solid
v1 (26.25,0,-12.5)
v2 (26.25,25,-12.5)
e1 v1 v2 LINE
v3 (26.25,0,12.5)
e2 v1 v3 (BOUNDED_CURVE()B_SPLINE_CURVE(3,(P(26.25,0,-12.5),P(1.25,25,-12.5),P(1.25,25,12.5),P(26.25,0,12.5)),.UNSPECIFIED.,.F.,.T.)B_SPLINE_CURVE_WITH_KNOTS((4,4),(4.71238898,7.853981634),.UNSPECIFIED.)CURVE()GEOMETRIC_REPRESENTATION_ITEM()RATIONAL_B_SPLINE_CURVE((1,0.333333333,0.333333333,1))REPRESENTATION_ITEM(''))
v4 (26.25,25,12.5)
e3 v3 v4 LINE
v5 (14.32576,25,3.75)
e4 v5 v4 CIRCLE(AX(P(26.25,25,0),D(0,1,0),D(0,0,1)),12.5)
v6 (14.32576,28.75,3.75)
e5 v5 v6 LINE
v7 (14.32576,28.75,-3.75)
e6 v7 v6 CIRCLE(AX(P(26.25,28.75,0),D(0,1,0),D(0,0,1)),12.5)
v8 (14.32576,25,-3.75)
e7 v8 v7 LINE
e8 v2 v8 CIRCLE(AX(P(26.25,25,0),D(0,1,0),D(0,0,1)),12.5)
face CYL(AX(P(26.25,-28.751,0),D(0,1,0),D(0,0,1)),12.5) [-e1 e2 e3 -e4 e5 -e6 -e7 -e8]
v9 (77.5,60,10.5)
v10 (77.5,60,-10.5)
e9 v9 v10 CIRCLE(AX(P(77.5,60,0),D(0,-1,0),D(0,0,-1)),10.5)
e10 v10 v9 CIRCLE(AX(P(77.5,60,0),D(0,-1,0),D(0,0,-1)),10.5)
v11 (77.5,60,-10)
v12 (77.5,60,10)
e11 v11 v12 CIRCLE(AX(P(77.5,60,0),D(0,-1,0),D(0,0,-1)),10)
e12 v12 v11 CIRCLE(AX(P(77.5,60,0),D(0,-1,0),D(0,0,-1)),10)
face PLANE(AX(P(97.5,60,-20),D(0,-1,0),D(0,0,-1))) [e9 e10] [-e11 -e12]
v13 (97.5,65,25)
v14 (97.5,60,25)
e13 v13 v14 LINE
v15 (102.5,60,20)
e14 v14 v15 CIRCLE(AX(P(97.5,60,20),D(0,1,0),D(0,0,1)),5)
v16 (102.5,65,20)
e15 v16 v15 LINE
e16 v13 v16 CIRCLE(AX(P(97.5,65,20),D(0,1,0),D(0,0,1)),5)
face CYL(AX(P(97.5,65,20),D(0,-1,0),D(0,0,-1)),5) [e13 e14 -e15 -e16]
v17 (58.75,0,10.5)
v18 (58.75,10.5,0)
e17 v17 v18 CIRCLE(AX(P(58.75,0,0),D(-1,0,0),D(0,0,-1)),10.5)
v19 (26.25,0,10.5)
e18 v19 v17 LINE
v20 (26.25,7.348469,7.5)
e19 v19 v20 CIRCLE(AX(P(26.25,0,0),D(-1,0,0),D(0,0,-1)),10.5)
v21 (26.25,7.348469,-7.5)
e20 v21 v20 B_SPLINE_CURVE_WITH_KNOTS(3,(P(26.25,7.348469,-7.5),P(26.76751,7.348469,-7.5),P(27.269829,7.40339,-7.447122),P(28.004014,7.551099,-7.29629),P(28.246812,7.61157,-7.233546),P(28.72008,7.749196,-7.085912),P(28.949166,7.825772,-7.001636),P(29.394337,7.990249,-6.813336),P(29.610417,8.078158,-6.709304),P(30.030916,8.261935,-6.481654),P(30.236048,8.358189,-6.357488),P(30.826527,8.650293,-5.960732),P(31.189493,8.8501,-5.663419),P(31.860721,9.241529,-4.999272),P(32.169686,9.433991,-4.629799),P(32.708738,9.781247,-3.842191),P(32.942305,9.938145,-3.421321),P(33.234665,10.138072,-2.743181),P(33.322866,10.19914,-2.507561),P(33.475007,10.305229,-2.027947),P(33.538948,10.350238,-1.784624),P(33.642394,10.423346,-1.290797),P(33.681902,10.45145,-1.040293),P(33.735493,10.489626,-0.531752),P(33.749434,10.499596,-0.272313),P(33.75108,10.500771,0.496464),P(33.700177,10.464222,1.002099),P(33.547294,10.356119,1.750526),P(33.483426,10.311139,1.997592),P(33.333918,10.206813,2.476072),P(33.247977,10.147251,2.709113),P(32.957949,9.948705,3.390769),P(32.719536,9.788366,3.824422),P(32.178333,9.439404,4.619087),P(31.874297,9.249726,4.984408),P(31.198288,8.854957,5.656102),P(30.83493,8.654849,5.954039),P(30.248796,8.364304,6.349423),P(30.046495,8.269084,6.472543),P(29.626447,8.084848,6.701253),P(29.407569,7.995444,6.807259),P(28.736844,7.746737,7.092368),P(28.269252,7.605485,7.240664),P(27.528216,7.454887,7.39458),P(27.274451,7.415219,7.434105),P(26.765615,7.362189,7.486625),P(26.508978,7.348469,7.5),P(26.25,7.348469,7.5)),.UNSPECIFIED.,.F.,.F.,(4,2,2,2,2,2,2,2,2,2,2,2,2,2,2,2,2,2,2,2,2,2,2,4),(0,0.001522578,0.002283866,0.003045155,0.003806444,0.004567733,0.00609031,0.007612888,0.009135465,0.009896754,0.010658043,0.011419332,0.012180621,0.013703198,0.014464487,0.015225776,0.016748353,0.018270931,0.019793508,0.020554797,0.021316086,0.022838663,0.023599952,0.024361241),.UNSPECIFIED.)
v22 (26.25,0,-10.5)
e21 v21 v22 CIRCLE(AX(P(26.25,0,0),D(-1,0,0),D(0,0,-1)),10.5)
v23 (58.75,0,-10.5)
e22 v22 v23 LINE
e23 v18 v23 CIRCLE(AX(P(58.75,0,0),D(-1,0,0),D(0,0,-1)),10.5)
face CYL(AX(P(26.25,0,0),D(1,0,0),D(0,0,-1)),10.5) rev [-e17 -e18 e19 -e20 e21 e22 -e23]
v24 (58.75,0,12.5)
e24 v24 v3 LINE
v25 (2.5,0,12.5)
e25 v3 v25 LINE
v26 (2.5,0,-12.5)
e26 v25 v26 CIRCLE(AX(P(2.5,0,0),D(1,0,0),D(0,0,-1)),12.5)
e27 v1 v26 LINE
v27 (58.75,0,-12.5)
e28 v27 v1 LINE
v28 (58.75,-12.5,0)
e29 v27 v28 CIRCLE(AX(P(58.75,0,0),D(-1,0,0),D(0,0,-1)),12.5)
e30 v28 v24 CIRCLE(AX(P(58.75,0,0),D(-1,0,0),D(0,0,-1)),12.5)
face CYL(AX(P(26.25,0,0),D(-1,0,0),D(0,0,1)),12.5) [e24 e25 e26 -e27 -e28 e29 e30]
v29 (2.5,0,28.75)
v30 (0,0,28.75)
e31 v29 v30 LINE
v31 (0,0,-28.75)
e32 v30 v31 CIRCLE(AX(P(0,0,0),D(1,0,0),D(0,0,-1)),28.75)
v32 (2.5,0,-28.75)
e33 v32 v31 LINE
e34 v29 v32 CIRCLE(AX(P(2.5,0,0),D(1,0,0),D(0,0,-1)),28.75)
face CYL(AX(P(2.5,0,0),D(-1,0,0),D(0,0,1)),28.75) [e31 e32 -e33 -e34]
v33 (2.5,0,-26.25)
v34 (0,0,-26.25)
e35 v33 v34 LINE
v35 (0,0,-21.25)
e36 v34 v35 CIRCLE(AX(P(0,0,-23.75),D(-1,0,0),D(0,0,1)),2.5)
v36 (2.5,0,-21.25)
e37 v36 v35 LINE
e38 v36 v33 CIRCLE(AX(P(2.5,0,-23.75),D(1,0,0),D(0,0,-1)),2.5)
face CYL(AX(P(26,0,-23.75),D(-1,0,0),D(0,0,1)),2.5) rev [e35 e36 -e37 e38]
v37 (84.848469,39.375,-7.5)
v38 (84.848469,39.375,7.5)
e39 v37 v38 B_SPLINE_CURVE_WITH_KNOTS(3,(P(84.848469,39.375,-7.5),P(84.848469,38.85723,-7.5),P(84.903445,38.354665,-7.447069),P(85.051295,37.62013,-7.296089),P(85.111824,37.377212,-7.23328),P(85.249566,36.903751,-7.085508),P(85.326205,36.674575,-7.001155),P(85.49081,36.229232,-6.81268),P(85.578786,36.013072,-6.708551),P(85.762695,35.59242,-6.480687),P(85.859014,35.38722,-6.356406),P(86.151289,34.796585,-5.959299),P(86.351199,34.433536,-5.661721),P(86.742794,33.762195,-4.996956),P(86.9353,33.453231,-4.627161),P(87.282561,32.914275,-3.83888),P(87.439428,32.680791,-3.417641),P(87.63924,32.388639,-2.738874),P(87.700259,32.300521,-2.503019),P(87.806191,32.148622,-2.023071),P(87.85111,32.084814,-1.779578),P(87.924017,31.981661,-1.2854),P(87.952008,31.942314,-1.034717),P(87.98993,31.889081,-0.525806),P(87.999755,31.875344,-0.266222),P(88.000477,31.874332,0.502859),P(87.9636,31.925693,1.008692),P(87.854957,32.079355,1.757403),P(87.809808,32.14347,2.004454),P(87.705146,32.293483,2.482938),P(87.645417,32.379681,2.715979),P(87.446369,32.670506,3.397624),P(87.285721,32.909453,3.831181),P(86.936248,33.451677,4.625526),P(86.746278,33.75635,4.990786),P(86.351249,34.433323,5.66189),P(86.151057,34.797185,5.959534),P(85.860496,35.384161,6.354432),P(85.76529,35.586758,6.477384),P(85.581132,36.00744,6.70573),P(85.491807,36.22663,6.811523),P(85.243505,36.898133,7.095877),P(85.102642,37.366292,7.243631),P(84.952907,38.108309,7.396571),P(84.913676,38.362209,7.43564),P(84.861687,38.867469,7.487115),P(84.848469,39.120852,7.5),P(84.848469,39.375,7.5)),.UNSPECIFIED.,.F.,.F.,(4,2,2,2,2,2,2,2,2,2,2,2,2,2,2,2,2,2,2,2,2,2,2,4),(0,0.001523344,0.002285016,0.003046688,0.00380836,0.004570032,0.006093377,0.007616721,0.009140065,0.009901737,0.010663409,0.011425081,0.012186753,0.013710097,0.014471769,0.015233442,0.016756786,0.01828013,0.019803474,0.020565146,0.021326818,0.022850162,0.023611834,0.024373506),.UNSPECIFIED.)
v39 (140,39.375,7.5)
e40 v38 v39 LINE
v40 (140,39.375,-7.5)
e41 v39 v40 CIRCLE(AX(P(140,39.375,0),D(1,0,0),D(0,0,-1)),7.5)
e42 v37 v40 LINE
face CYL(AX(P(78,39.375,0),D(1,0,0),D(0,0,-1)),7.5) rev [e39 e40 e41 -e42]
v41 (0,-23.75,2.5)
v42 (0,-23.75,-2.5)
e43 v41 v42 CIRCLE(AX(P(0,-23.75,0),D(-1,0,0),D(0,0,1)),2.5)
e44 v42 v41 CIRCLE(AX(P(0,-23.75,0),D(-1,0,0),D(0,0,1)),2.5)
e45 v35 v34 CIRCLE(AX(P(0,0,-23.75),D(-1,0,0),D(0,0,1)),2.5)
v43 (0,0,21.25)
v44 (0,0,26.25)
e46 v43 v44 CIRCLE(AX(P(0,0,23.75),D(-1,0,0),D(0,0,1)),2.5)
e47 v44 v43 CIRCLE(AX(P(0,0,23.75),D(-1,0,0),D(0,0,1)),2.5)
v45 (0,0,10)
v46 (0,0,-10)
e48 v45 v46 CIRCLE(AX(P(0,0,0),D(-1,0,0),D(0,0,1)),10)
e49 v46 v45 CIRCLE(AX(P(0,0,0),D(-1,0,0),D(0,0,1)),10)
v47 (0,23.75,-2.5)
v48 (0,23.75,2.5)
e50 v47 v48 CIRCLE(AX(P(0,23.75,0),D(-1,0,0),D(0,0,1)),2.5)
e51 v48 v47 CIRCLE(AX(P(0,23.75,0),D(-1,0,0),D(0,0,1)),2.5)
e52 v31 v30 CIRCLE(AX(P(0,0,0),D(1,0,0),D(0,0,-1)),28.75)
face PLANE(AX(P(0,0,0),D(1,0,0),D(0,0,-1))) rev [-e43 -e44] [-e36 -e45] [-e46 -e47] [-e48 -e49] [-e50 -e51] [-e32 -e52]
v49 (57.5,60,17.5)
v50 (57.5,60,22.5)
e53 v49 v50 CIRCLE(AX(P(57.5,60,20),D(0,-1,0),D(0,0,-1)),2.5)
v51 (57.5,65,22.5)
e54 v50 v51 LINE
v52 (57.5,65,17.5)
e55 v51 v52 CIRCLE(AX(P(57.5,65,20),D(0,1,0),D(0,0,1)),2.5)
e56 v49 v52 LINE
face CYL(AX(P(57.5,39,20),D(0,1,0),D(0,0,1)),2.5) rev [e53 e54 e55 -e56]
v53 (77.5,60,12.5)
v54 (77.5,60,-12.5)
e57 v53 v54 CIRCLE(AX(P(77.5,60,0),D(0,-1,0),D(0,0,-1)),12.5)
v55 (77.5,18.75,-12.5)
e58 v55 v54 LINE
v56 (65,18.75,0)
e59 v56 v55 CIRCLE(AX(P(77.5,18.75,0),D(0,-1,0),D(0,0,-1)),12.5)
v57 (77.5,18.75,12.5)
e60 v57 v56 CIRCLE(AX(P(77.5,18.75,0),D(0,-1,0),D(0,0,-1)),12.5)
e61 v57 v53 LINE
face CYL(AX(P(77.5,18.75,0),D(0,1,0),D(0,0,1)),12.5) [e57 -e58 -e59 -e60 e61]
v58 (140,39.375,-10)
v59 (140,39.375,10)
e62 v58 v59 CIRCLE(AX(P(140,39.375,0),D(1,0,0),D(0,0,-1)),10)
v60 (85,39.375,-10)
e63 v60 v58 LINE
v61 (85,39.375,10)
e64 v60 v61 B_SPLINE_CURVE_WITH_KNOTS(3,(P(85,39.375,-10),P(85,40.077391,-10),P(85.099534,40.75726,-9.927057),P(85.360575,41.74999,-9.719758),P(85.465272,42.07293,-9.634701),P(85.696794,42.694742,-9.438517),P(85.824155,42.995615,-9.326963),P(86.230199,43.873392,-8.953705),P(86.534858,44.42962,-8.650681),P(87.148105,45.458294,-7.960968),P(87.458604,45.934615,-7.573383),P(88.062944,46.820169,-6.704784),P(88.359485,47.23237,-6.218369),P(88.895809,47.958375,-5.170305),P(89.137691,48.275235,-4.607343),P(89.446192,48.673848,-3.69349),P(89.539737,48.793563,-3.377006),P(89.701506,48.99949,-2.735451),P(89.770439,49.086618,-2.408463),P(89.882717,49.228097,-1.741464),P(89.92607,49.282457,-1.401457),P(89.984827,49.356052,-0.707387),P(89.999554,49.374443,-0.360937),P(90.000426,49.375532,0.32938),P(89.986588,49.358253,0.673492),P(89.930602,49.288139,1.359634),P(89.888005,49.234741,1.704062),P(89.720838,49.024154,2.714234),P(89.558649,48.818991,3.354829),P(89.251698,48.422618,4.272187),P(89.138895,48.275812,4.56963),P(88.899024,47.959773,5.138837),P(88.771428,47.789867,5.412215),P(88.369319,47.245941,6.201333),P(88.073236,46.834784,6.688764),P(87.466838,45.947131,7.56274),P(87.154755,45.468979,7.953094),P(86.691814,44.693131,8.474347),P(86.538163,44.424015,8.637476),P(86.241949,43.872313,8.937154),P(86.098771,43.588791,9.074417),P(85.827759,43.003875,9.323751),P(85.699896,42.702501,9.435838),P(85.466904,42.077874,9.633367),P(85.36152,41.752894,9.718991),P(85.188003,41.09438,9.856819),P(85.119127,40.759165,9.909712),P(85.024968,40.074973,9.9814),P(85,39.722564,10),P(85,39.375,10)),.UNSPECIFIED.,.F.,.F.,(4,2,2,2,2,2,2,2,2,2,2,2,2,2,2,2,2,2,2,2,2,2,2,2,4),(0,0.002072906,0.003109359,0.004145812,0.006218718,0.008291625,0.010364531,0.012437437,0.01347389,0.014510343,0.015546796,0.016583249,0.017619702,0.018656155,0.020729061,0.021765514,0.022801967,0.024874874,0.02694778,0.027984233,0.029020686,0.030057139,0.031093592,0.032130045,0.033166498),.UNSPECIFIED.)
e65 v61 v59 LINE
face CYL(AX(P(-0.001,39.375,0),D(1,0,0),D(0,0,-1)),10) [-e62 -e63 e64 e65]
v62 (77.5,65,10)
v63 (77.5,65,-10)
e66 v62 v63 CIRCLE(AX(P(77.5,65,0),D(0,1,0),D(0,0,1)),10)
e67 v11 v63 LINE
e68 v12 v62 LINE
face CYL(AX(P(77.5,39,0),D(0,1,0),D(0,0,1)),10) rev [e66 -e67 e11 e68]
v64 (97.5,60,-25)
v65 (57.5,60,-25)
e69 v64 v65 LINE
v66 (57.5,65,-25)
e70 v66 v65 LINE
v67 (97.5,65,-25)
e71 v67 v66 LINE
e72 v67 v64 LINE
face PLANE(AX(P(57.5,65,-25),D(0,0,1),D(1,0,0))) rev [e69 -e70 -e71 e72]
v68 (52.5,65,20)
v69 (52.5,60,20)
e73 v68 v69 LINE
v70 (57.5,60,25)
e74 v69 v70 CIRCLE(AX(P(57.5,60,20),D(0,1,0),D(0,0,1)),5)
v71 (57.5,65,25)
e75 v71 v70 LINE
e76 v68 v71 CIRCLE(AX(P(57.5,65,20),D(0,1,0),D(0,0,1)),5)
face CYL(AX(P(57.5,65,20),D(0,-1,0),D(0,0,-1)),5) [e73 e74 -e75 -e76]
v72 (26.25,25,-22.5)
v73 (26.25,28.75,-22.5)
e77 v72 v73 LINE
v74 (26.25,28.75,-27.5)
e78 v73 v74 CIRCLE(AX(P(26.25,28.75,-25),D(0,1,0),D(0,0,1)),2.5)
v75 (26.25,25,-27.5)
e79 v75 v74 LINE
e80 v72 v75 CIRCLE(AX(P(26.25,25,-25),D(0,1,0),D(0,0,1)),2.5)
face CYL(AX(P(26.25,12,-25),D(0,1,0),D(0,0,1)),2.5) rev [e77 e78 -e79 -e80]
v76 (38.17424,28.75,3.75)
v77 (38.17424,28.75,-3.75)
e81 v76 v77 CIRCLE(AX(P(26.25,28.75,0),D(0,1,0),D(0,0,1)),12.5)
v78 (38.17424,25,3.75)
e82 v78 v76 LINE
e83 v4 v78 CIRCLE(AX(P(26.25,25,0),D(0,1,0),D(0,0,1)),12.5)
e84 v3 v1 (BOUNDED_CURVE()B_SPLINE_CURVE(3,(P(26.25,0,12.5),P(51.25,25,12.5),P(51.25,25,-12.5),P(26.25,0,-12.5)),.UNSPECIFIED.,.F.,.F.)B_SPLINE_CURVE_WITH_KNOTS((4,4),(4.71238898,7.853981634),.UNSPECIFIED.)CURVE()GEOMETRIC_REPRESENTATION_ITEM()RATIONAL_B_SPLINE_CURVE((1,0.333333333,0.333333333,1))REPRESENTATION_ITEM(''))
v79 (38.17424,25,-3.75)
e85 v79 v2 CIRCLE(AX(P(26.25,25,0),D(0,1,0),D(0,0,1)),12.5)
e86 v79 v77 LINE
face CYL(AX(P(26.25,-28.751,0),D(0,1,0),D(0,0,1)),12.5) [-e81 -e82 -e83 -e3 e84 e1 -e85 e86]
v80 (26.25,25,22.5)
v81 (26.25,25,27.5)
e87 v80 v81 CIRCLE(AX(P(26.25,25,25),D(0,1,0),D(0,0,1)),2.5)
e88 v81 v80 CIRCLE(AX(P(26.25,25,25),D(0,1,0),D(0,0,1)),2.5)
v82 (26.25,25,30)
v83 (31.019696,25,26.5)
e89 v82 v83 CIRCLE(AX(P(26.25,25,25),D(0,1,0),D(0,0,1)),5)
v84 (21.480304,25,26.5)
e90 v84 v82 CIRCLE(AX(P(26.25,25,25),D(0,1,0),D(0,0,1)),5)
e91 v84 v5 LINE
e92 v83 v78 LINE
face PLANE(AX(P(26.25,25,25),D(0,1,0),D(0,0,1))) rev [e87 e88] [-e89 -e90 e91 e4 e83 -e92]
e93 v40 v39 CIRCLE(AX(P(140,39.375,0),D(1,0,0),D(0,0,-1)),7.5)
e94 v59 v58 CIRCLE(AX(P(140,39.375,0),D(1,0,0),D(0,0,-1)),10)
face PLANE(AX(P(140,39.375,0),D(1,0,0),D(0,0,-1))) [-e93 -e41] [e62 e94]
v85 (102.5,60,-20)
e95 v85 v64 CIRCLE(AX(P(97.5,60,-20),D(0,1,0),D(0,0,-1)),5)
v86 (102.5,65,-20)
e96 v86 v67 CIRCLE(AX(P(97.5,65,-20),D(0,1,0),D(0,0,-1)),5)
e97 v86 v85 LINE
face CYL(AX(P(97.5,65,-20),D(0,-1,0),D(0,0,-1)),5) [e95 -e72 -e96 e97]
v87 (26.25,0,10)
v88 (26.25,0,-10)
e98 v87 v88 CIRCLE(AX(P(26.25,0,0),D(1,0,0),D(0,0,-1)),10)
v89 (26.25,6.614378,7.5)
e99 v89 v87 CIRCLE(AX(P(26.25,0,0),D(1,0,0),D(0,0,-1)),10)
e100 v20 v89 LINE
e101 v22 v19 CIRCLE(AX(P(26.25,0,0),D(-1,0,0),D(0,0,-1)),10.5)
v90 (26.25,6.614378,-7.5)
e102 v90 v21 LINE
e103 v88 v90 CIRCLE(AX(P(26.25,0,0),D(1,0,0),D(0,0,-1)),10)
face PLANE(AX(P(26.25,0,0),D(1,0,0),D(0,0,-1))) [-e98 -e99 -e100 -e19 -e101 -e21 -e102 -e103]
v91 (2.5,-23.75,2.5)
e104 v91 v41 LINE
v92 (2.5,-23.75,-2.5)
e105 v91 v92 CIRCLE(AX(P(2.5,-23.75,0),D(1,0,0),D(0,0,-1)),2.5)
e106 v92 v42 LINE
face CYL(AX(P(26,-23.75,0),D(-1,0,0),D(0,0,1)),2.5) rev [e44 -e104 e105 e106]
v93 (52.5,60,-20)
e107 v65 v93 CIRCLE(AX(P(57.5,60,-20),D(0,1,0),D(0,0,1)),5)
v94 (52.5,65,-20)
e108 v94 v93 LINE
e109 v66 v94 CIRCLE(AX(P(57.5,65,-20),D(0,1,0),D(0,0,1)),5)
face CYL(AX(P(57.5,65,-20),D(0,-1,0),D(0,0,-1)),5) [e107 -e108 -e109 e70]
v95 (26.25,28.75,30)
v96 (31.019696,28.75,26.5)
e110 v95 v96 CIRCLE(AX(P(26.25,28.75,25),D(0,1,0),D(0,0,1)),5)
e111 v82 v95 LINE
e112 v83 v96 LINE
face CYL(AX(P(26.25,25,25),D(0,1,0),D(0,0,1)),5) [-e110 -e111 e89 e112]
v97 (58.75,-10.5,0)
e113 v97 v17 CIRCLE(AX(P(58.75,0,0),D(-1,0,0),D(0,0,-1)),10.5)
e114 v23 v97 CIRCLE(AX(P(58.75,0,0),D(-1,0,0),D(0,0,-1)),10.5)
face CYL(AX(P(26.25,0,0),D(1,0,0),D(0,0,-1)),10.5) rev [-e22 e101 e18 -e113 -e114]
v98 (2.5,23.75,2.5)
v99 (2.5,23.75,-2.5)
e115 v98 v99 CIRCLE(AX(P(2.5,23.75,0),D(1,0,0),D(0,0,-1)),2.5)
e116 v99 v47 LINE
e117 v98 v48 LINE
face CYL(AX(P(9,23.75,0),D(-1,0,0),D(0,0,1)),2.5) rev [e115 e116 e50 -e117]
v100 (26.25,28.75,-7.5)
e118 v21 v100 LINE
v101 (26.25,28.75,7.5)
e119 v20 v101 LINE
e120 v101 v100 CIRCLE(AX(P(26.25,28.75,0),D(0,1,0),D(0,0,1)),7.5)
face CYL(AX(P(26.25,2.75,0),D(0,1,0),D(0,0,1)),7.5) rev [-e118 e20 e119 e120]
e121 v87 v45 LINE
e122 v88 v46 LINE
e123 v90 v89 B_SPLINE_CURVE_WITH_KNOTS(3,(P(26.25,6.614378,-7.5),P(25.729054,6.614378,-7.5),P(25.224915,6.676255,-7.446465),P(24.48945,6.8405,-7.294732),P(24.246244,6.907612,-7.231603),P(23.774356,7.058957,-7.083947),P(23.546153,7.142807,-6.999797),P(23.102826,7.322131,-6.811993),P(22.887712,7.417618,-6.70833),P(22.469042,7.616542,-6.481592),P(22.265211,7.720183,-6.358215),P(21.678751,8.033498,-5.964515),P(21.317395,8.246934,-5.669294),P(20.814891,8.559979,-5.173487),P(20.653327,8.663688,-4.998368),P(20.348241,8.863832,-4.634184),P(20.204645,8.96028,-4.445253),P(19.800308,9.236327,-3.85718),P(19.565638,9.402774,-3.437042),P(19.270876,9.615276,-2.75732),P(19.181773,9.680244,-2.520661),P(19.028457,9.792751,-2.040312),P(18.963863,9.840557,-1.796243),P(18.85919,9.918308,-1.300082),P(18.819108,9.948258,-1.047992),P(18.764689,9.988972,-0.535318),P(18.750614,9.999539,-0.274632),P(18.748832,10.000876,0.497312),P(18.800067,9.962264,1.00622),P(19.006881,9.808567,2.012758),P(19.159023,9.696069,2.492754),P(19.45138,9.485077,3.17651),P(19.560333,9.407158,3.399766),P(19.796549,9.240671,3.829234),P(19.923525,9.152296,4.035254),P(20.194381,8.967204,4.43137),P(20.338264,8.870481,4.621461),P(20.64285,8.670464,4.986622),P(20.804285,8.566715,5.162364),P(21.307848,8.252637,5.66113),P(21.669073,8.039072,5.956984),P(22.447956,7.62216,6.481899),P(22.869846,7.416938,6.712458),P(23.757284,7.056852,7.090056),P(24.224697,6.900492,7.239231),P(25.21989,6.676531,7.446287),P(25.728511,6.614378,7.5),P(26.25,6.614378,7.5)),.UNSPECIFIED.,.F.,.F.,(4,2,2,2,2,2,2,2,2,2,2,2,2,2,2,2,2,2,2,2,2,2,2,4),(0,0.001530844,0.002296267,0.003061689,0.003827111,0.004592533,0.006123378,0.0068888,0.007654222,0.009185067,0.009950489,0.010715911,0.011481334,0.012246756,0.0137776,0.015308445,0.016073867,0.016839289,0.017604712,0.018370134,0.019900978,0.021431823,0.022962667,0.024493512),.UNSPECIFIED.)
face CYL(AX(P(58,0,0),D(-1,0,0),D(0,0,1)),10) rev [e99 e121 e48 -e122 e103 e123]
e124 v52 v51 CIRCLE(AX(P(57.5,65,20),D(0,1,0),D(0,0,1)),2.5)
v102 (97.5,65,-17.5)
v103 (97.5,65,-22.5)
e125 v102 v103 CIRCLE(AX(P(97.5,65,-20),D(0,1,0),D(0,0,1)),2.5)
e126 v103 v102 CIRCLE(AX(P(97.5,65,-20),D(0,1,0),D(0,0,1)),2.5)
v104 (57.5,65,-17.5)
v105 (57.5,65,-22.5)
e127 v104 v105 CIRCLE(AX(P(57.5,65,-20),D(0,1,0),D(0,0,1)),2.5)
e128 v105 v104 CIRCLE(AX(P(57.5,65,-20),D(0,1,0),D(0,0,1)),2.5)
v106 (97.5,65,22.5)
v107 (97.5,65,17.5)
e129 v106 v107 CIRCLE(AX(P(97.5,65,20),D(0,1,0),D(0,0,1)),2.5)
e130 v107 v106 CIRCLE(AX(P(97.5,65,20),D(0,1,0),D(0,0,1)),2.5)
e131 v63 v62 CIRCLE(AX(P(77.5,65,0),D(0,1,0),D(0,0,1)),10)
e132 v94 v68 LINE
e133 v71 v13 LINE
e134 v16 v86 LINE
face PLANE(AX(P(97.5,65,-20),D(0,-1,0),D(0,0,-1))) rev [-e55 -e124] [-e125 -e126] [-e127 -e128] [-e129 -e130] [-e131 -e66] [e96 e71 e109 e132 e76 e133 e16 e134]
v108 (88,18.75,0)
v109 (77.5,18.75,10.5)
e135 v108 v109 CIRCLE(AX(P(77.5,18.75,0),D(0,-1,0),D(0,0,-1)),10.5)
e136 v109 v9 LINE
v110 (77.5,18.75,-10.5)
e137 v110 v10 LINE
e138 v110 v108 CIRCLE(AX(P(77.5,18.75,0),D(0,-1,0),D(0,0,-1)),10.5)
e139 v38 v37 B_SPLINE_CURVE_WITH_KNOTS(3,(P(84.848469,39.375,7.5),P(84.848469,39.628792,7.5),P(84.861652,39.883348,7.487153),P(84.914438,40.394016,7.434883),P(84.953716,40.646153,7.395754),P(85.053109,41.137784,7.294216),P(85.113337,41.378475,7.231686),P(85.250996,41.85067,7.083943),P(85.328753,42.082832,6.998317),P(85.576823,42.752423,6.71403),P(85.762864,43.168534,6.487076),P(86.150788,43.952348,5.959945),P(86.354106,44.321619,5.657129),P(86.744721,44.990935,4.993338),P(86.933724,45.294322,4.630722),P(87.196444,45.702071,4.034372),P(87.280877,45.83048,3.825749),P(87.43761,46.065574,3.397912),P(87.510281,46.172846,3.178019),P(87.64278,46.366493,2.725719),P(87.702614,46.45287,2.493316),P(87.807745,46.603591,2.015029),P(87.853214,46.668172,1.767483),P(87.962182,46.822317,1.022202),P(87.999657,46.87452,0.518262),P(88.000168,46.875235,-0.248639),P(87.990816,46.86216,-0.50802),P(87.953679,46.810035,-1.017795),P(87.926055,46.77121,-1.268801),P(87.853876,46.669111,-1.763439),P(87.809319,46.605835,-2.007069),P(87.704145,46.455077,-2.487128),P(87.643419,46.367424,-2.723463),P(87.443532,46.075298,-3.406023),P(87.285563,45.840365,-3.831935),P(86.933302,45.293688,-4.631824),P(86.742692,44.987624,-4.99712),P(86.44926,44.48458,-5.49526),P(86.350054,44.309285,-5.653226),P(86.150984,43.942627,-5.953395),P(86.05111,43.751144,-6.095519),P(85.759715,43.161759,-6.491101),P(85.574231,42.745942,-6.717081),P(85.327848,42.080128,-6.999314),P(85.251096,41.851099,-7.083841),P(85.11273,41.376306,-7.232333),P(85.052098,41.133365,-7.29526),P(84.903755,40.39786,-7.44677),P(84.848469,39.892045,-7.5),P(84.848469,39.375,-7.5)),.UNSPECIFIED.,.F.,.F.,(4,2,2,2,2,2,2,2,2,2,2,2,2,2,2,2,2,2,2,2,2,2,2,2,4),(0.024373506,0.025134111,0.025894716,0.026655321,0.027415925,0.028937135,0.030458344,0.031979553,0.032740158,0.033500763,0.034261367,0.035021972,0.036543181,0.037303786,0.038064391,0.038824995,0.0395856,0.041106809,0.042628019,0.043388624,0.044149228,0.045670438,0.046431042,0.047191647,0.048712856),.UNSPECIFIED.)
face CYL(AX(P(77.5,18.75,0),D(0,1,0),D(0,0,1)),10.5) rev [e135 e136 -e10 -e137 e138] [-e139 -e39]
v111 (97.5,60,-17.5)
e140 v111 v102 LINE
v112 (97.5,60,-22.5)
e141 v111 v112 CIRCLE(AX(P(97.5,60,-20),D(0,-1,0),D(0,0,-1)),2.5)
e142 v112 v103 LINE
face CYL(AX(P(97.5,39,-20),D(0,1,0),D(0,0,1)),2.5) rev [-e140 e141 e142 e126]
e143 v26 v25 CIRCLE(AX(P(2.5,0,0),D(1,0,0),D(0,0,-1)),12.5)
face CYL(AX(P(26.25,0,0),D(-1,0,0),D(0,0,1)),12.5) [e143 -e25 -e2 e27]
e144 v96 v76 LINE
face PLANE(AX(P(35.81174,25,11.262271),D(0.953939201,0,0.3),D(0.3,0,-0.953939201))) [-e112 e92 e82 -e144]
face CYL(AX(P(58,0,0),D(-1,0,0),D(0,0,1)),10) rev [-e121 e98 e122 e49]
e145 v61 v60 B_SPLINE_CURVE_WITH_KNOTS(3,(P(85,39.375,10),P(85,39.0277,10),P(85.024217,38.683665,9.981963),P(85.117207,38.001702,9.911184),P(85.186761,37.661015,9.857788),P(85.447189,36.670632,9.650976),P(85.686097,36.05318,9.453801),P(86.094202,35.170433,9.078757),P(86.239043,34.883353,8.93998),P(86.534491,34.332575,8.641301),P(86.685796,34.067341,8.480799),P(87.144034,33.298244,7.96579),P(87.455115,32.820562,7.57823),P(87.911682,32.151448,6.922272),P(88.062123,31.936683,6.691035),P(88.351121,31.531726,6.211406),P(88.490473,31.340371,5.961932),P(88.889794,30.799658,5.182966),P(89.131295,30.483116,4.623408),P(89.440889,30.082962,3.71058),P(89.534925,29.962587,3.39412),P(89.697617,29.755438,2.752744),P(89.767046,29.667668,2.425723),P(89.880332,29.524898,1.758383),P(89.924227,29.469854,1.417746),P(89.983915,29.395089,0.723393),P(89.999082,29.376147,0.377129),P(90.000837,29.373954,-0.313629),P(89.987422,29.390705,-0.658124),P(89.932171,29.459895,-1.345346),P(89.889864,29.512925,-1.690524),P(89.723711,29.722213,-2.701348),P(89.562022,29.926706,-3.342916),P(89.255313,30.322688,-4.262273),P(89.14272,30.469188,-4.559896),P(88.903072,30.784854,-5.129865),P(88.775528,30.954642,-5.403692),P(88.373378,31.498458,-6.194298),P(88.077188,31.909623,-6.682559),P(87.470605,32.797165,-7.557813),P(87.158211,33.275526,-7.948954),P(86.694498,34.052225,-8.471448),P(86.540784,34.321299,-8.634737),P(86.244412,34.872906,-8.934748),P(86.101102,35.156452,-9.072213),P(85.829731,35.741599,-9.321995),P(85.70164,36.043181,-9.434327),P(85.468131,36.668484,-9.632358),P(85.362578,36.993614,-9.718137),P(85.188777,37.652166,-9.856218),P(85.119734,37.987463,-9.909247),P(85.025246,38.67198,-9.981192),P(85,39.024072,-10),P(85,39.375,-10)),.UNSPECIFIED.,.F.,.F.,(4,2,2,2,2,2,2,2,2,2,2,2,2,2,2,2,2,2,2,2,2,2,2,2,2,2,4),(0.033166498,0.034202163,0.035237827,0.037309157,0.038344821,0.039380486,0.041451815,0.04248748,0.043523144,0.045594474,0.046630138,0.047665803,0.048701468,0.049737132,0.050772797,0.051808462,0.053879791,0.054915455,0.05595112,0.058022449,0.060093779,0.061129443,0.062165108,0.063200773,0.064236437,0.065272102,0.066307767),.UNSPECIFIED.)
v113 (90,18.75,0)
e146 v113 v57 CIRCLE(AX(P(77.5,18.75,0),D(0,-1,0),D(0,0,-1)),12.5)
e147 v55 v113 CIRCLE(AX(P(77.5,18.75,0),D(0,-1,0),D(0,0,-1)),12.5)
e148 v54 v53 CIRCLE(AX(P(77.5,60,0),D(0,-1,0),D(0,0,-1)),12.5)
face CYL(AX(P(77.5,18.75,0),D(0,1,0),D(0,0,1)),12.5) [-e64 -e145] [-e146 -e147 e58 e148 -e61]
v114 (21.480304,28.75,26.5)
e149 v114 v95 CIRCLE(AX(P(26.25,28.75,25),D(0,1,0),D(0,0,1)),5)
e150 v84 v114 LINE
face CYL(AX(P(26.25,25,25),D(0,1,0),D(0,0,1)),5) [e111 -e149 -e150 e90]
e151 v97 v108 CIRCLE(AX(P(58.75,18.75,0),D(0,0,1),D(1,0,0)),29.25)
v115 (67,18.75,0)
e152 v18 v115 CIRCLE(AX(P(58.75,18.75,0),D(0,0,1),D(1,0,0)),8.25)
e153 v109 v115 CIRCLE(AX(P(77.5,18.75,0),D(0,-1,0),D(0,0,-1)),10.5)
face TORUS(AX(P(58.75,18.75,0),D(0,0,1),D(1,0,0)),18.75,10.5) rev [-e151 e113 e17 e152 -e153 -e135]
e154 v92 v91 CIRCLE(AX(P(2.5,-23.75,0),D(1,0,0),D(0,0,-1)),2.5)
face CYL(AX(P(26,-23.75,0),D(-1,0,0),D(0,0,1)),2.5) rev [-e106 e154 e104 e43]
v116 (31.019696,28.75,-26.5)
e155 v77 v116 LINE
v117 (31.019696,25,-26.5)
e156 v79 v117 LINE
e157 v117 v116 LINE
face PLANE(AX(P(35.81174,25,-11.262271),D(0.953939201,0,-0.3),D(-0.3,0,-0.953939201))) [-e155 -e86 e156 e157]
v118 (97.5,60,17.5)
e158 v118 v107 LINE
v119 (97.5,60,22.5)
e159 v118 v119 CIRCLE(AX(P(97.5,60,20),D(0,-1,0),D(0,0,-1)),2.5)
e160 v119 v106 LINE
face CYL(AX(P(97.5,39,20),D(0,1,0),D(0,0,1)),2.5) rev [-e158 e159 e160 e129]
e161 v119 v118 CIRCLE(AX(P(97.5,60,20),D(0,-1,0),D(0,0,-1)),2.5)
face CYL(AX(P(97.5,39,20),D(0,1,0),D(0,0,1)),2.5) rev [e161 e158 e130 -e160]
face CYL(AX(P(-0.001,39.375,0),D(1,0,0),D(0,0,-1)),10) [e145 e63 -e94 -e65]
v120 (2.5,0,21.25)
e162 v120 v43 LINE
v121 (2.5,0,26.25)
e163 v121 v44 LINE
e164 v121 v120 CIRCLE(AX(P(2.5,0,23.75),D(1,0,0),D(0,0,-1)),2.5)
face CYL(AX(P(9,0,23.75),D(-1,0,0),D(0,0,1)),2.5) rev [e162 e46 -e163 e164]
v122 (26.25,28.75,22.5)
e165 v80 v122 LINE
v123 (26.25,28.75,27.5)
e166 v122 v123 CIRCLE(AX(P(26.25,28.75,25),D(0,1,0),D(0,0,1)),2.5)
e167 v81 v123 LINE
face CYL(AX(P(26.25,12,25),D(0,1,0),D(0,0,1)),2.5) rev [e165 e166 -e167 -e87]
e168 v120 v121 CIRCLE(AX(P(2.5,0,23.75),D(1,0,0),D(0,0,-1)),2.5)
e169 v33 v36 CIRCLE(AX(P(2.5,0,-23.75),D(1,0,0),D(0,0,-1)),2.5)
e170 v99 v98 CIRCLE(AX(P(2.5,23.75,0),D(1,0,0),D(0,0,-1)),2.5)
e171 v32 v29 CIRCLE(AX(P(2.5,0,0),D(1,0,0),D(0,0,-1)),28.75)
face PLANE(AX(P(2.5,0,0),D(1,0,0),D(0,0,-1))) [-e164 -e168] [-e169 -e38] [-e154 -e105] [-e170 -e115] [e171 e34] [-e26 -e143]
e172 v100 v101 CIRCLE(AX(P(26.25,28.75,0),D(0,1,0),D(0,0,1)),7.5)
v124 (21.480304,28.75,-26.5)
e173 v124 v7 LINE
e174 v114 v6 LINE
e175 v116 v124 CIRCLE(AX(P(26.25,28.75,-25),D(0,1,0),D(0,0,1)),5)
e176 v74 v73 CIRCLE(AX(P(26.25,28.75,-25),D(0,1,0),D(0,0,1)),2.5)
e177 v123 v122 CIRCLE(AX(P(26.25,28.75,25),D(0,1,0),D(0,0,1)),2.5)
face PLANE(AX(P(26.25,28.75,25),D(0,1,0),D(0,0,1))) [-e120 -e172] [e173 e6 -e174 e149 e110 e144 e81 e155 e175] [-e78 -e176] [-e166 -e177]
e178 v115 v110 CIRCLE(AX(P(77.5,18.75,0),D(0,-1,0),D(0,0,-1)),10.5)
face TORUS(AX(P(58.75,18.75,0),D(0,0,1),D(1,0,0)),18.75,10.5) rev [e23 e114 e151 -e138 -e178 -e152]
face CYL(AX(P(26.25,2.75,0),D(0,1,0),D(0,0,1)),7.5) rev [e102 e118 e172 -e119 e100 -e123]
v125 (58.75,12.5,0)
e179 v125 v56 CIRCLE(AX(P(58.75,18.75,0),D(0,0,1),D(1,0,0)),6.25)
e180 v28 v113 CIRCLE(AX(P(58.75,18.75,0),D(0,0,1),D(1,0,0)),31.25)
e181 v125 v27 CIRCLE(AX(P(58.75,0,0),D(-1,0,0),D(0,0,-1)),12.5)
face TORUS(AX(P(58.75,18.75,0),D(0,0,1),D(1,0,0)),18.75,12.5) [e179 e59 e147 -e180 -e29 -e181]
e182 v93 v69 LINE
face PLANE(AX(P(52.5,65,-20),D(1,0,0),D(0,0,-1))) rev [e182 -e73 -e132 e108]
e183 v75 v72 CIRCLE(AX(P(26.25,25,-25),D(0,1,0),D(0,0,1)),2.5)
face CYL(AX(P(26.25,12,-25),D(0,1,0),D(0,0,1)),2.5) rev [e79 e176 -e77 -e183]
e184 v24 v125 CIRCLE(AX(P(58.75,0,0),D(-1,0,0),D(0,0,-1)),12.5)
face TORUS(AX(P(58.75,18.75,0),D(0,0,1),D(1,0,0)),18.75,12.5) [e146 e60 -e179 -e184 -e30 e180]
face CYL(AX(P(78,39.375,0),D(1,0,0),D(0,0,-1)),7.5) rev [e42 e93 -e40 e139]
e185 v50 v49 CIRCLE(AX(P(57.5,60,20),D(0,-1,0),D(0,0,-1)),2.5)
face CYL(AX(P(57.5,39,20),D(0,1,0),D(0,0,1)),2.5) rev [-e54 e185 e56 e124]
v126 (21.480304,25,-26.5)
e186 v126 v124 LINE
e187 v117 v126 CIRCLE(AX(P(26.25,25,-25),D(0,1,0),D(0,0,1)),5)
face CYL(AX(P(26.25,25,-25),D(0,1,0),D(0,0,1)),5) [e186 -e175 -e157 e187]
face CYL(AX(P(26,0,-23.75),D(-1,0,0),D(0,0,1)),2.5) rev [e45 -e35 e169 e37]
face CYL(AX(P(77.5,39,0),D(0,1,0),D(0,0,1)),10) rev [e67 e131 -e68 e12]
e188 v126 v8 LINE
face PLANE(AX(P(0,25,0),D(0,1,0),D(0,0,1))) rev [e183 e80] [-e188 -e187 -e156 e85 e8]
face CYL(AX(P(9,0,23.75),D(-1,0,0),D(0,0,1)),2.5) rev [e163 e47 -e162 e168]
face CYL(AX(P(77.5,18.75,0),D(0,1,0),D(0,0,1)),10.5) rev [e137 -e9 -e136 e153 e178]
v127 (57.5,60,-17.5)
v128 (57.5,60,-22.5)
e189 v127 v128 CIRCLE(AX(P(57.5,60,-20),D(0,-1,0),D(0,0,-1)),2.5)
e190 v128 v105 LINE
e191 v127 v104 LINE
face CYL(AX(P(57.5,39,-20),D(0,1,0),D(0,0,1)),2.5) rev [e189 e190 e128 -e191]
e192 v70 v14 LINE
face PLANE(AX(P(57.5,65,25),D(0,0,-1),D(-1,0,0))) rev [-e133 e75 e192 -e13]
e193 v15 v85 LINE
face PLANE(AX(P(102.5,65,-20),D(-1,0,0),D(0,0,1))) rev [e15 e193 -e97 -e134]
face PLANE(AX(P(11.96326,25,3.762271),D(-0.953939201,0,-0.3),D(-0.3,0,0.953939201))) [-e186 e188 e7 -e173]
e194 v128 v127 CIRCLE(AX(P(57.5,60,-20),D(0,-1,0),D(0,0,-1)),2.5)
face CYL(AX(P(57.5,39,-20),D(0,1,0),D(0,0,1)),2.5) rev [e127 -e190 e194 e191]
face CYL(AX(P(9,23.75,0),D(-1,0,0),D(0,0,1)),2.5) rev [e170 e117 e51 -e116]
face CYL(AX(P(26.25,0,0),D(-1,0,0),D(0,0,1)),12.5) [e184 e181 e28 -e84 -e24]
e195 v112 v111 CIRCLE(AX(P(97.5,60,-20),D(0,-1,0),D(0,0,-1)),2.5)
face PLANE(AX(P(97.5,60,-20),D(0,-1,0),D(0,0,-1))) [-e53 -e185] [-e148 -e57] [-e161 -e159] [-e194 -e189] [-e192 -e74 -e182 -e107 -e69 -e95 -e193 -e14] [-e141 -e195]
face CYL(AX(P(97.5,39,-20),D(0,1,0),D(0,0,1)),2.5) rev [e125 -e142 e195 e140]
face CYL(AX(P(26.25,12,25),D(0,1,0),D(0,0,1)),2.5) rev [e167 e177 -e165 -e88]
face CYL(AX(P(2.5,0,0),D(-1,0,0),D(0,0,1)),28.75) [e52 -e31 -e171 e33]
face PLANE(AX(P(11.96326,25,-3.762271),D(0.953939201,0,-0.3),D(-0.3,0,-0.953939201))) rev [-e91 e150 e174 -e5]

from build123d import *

# Parameters (mm, degrees)
ROUND_FLANGE_SKETCH_R         = 28.75
ROUND_FLANGE_57_5_DEPTH       = 2.5
INLET_PIPE_SKETCH_R           = 10
INLET_PIPE_20_DEPTH           = 23.75
FLANGE_A_NECK_REACH           = 71.44
FLANGE_A_NECK_END_RADIUS      = 10
FLANGE_A_NECK_SKETCH_R        = 10
FLANGE_A_HUB_SKETCH_R         = 12.5
FLANGE_A_HUB_25_DEPTH         = 3.75
FLANGE_A_LUG_1_SKETCH_R       = 5
FLANGE_A_LUG_1_DEPTH          = 3.75
FLANGE_A_LUG_2_SKETCH_R       = 5
FLANGE_A_LUG_2_DEPTH          = 3.75
FLANGE_A_WEB_25X10_DEPTH      = 3.75
FLANGE_A_TRIM_SKETCH_W        = 46.981578054
FLANGE_A_TRIM_SKETCH_H        = 84.080147296
FLANGE_A_TRIM_CUT_DEPTH       = 80
OUTLET_PIPE_SKETCH_R          = 12.5
OUTLET_PIPE_25_DEPTH          = 23.75
FLANGE_B_HUB_25_REACH         = 71.44
FLANGE_B_HUB_25_END_RADIUS    = 12.5
FLANGE_B_HUB_SKETCH_R         = 12.5
FLANGE_B_LUG_1_SKETCH_R       = 5
FLANGE_B_LUG_1_DEPTH          = 3.75
FLANGE_B_LUG_2_SKETCH_R       = 5
FLANGE_B_LUG_2_DEPTH          = 3.75
FLANGE_B_WEB_1_25X10_DEPTH    = 3.75
FLANGE_B_WEB_2_10X25_DEPTH    = 3.75
FLANGE_B_LUG_1_HOLE_SKETCH_R  = 2.5
FLANGE_B_LUG_1_HOLE_5_DEPTH   = 16.75
FLANGE_B_LUG_2_HOLE_SKETCH_R  = 2.5
FLANGE_B_LUG_2_HOLE_5_DEPTH   = 16.75
ELBOW_PIPE_SWEEP_PROFILE_R    = 12.5
ELBOW_PIPE_SWEEP_PROFILE_R_2  = 10.5
SQUARE_FLANGE_50X50_DEPTH     = 5
ROUND_FLANGE_BORE_SKETCH_R    = 10
ROUND_FLANGE_BORE_DEPTH       = 58
FLANGE_B_BORE_SKETCH_R        = 7.5
FLANGE_B_BORE_15_DEPTH        = 26
SQUARE_FLANGE_BORE_SKETCH_R   = 10
SQUARE_FLANGE_BORE_20_DEPTH   = 26
SQUARE_FLANGE_HOLE_1_SKETCH_R = 2.5
SQUARE_FLANGE_HOLE_1_5_DEPTH  = 26
SQUARE_FLANGE_HOLE_2_SKETCH_R = 2.5
SQUARE_FLANGE_HOLE_2_5_DEPTH  = 26
SQUARE_FLANGE_HOLE_3_SKETCH_R = 2.5
SQUARE_FLANGE_HOLE_3_5_DEPTH  = 26
SQUARE_FLANGE_HOLE_4_SKETCH_R = 2.5
SQUARE_FLANGE_HOLE_4_5_DEPTH  = 26
ROUND_FLANGE_HOLE_1_SKETCH_R  = 2.5
ROUND_FLANGE_HOLE_1_5_DEPTH   = 26
ROUND_FLANGE_HOLE_2_SKETCH_R  = 2.5
ROUND_FLANGE_HOLE_2_5_DEPTH   = 26
ROUND_FLANGE_HOLE_3_SKETCH_R  = 2.5
ROUND_FLANGE_HOLE_3_5_DEPTH   = 9
ROUND_FLANGE_HOLE_4_SKETCH_R  = 2.5
ROUND_FLANGE_HOLE_4_5_DEPTH   = 9
SIDE_PIPE_20_REACH            = 160.559
SIDE_PIPE_20_END_RADIUS       = 12.5
SIDE_PIPE_SKETCH_R            = 10
SIDE_PIPE_BORE_SKETCH_R       = 7.5
SIDE_PIPE_BORE_15_DEPTH       = 62


with BuildPart() as part:
    # Round Flange Sketch → Round Flange _57.5 (new body)
    with BuildSketch(Plane(origin=(0, 0, 0), x_dir=(0, 0, -1), z_dir=(1, 0, 0))):
        Circle(ROUND_FLANGE_SKETCH_R)
    extrude(amount=ROUND_FLANGE_57_5_DEPTH)

    # Inlet Pipe Sketch → Inlet Pipe _20 (add)
    with BuildSketch(Plane(origin=(2.5, 0, 0), x_dir=(0, 0, -1), z_dir=(1, 0, 0))):
        Circle(INLET_PIPE_SKETCH_R)
    extrude(amount=INLET_PIPE_20_DEPTH)

    # Flange A Neck: up to this cylinder (the profile starts outside it)
    flange_a_neck_end = Plane(origin=(26.25, 0, 0), z_dir=(-1, 0, 0)) * Cylinder(FLANGE_A_NECK_END_RADIUS, 163.88, mode=Mode.PRIVATE)
    # Flange A Neck Sketch → Flange A Neck (add, up to the surface)
    with BuildSketch(Plane(origin=(0, 28.75, 0), x_dir=(1, 0, 0), z_dir=(0, 1, 0)), mode=Mode.PRIVATE) as flange_a_neck_sk1:
        with Locations(Location((26.25, 0, 0), (0, 0, 270))):
            Circle(FLANGE_A_NECK_SKETCH_R)
    flange_a_neck_tool1 = extrude(flange_a_neck_sk1.sketch, amount=-FLANGE_A_NECK_REACH, mode=Mode.PRIVATE) - flange_a_neck_end
    add(flange_a_neck_tool1.solids().sort_by_distance((26.25, 28.75, 0))[0])

    # Flange A Hub Sketch → Flange A Hub _25 (add)
    with BuildSketch(Plane(origin=(0, 28.75, 0), x_dir=(1, 0, 0), z_dir=(0, 1, 0))):
        with Locations(Location((26.25, 0, 0), (0, 0, 270))):
            Circle(FLANGE_A_HUB_SKETCH_R)
    extrude(amount=-FLANGE_A_HUB_25_DEPTH)



with BuildPart() as body_2:
    # Flange A Lug 1 Sketch → Flange A Lug 1 (new body)
    with BuildSketch(Plane(origin=(0, 28.75, 0), x_dir=(1, 0, 0), z_dir=(0, 1, 0))):
        with Locations(Location((26.25, -25, 0), (0, 0, 270))):
            Circle(FLANGE_A_LUG_1_SKETCH_R)
    extrude(amount=-FLANGE_A_LUG_1_DEPTH)


with BuildPart() as body_3:
    # Flange A Lug 2 Sketch → Flange A Lug 2 (new body)
    with BuildSketch(Plane(origin=(0, 28.75, 0), x_dir=(1, 0, 0), z_dir=(0, 1, 0))):
        with Locations(Location((26.740993145, 25, 0), (0, 0, 270))):
            Circle(FLANGE_A_LUG_2_SKETCH_R)
    extrude(amount=-FLANGE_A_LUG_2_DEPTH)


with BuildPart() as part_1:
    add(part.part)

    add(body_2.part)  # Flange A Web 25x10 merges body 2
    # Flange A Web Sketch → Flange A Web 25x10 (add)
    with BuildSketch(Plane(origin=(0, 28.75, 0), x_dir=(1, 0, 0), z_dir=(0, 1, 0))):
        with BuildLine():
            ThreePointArc((38.174240018, -3.75), (26.25, -12.5), (14.325759982, -3.75))
            Line((14.325759982, -3.75), (21.480303993, -26.5))
            ThreePointArc((21.480303993, -26.5), (25.491211504, -20.057911371), (31.25, -25))
            ThreePointArc((31.25, -25), (31.192088629, -25.758788496), (31.019696007, -26.5))
            Line((31.019696007, -26.5), (38.174240018, -3.75))
        make_face()
    extrude(amount=-FLANGE_A_WEB_25X10_DEPTH)


with BuildPart() as flange_a_trim_cut_tool:
    # Flange A Trim Sketch → Flange A Trim Cut (new body)
    with BuildSketch(Plane(origin=(0, 28.75, 0), x_dir=(1, 0, 0), z_dir=(0, 1, 0))):
        with Locations((25.990789027, 3.010416982)):
            Rectangle(FLANGE_A_TRIM_SKETCH_W, FLANGE_A_TRIM_SKETCH_H)
    extrude(amount=-FLANGE_A_TRIM_CUT_DEPTH)


with BuildPart() as part_2:
    add(part_1.part)

    # Flange A Trim Cut: cut by flange_a_trim_cut_tool
    add(flange_a_trim_cut_tool.part, mode=Mode.SUBTRACT)

    # Outlet Pipe Sketch → Outlet Pipe _25 (add)
    with BuildSketch(Plane(origin=(2.5, 0, 0), x_dir=(0, 0, -1), z_dir=(1, 0, 0))):
        Circle(OUTLET_PIPE_SKETCH_R)
    extrude(amount=OUTLET_PIPE_25_DEPTH)

    # Flange B Hub _25: up to this cylinder (the profile starts outside it)
    flange_b_hub_25_end = Plane(origin=(26.25, 0, 0), z_dir=(-1, 0, 0)) * Cylinder(FLANGE_B_HUB_25_END_RADIUS, 168.88, mode=Mode.PRIVATE)
    # Flange B Hub Sketch → Flange B Hub _25 (add, up to the surface)
    with BuildSketch(Plane(origin=(0, 28.75, 0), x_dir=(1, 0, 0), z_dir=(0, 1, 0)), mode=Mode.PRIVATE) as flange_b_hub_25_sk1:
        with Locations(Location((26.25, 0, 0), (0, 0, 270))):
            Circle(FLANGE_B_HUB_SKETCH_R)
    flange_b_hub_25_tool1 = extrude(flange_b_hub_25_sk1.sketch, amount=-FLANGE_B_HUB_25_REACH, mode=Mode.PRIVATE) - flange_b_hub_25_end
    add(flange_b_hub_25_tool1.solids().sort_by_distance((26.25, 28.75, 0))[0])



with BuildPart() as body_3_1:
    add(body_3.part)

    # Flange A Trim Cut: cut by flange_a_trim_cut_tool
    add(flange_a_trim_cut_tool.part, mode=Mode.SUBTRACT)


with BuildPart() as body_2_2:
    # Flange B Lug 1 Sketch → Flange B Lug 1 (new body)
    with BuildSketch(Plane(origin=(0, 28.75, 0), x_dir=(1, 0, 0), z_dir=(0, 1, 0))):
        with Locations(Location((26.25, 25, 0), (0, 0, 270))):
            Circle(FLANGE_B_LUG_1_SKETCH_R)
    extrude(amount=-FLANGE_B_LUG_1_DEPTH)


with BuildPart() as body_3_2:
    # Flange B Lug 2 Sketch → Flange B Lug 2 (new body)
    with BuildSketch(Plane(origin=(0, 28.75, 0), x_dir=(1, 0, 0), z_dir=(0, 1, 0))):
        with Locations(Location((26.25, -25, 0), (0, 0, 270))):
            Circle(FLANGE_B_LUG_2_SKETCH_R)
    extrude(amount=-FLANGE_B_LUG_2_DEPTH)


with BuildPart() as part_3:
    add(part_2.part)

    add(body_2_2.part)  # Flange B Web 1 25x10 merges body 2 2
    # Flange B Web 1 Sketch → Flange B Web 1 25x10 (add)
    with BuildSketch(Plane(origin=(0, 28.75, 0), x_dir=(1, 0, 0), z_dir=(0, 1, 0))):
        with BuildLine():
            ThreePointArc((31.25, 25), (25.491211504, 20.057911371), (21.480303993, 26.5))
            Line((21.480303993, 26.5), (14.325759982, 3.75))
            ThreePointArc((14.325759982, 3.75), (26.25, 12.5), (38.174240018, 3.75))
            Line((38.174240018, 3.75), (31.019696007, 26.5))
            ThreePointArc((31.019696007, 26.5), (31.192088629, 25.758788496), (31.25, 25))
        make_face()
    extrude(amount=-FLANGE_B_WEB_1_25X10_DEPTH)


    add(body_3_2.part)  # Flange B Web 2 10x25 merges body 3 2
    # Flange B Web 2 Sketch → Flange B Web 2 10x25 (add)
    with BuildSketch(Plane(origin=(0, 28.75, 0), x_dir=(1, 0, 0), z_dir=(0, 1, 0))):
        with BuildLine():
            Line((14.325759982, -3.75), (21.480303993, -26.5))
            ThreePointArc((21.480303993, -26.5), (25.491211504, -20.057911371), (31.25, -25))
            ThreePointArc((31.25, -25), (31.192088629, -25.758788496), (31.019696007, -26.5))
            Line((31.019696007, -26.5), (38.174240018, -3.75))
            ThreePointArc((38.174240018, -3.75), (26.25, -12.5), (14.325759982, -3.75))
        make_face()
    extrude(amount=-FLANGE_B_WEB_2_10X25_DEPTH)

    # Flange B Lug 1 Hole Sketch → Flange B Lug 1 Hole _5 (cut)
    with BuildSketch(Plane(origin=(0, 28.75, 0), x_dir=(1, 0, 0), z_dir=(0, 1, 0))):
        with Locations(Location((26.25, 25, 0), (0, 0, 270))):
            Circle(FLANGE_B_LUG_1_HOLE_SKETCH_R)
    extrude(amount=-FLANGE_B_LUG_1_HOLE_5_DEPTH, mode=Mode.SUBTRACT)

    # Flange B Lug 2 Hole Sketch → Flange B Lug 2 Hole _5 (cut)
    with BuildSketch(Plane(origin=(0, 28.75, 0), x_dir=(1, 0, 0), z_dir=(0, 1, 0))):
        with Locations(Location((26.25, -25, 0), (0, 0, 270))):
            Circle(FLANGE_B_LUG_2_HOLE_SKETCH_R)
    extrude(amount=-FLANGE_B_LUG_2_HOLE_5_DEPTH, mode=Mode.SUBTRACT)

    # Elbow Pipe Sweep: sweep along a path in Elbow Path Sketch
    with BuildLine(Plane.XY) as elbow_pipe_sweep_path:
        Line((26.25, 0), (58.75, 0))
        ThreePointArc((58.75, 0), (72.008252147, 5.491747853), (77.5, 18.75))
        Line((77.5, 18.75), (77.5, 60))
    # Elbow Pipe Sweep profile (on start of the path) → Elbow Pipe Sweep (sweep)
    with BuildSketch(Plane(origin=(26.25, 0, 0), x_dir=(0, 0, 1), z_dir=(1, 0, 0))):
        Circle(ELBOW_PIPE_SWEEP_PROFILE_R)
        Circle(ELBOW_PIPE_SWEEP_PROFILE_R_2, mode=Mode.SUBTRACT)
    sweep(path=elbow_pipe_sweep_path.line)

    # Square Flange Sketch → Square Flange 50x50 (add)
    with BuildSketch(Plane(origin=(0, 60, 0), x_dir=(1, 0, 0), z_dir=(0, 1, 0))):
        with BuildLine():
            Line((57.5, 25), (97.5, 25))
            ThreePointArc((97.5, 25), (101.035533906, 23.535533906), (102.5, 20))
            Line((102.5, 20), (102.5, -20))
            ThreePointArc((102.5, -20), (101.035533906, -23.535533906), (97.5, -25))
            Line((97.5, -25), (57.5, -25))
            ThreePointArc((57.5, -25), (53.964466094, -23.535533906), (52.5, -20))
            Line((52.5, -20), (52.5, 20))
            ThreePointArc((52.5, 20), (53.964466094, 23.535533906), (57.5, 25))
        make_face()
    extrude(amount=SQUARE_FLANGE_50X50_DEPTH)

    # Round Flange Bore Sketch → Round Flange Bore (cut)
    with BuildSketch(Plane.ZY):
        Circle(ROUND_FLANGE_BORE_SKETCH_R)
    extrude(amount=-ROUND_FLANGE_BORE_DEPTH, mode=Mode.SUBTRACT)

    # Flange B Bore Sketch → Flange B Bore _15 (cut)
    with BuildSketch(Plane(origin=(0, 28.75, 0), x_dir=(1, 0, 0), z_dir=(0, 1, 0))):
        with Locations(Location((26.25, 0, 0), (0, 0, 270))):
            Circle(FLANGE_B_BORE_SKETCH_R)
    extrude(amount=-FLANGE_B_BORE_15_DEPTH, mode=Mode.SUBTRACT)

    # Square Flange Bore Sketch → Square Flange Bore _20 (cut)
    with BuildSketch(Plane(origin=(0, 65, 0), x_dir=(1, 0, 0), z_dir=(0, 1, 0))):
        with Locations(Location((77.5, 0, 0), (0, 0, 270))):
            Circle(SQUARE_FLANGE_BORE_SKETCH_R)
    extrude(amount=-SQUARE_FLANGE_BORE_20_DEPTH, mode=Mode.SUBTRACT)

    # Square Flange Hole 1 Sketch → Square Flange Hole 1 _5 (cut)
    with BuildSketch(Plane(origin=(0, 65, 0), x_dir=(1, 0, 0), z_dir=(0, 1, 0))):
        with Locations(Location((57.5, 20, 0), (0, 0, 270))):
            Circle(SQUARE_FLANGE_HOLE_1_SKETCH_R)
    extrude(amount=-SQUARE_FLANGE_HOLE_1_5_DEPTH, mode=Mode.SUBTRACT)

    # Square Flange Hole 2 Sketch → Square Flange Hole 2 _5 (cut)
    with BuildSketch(Plane(origin=(0, 65, 0), x_dir=(1, 0, 0), z_dir=(0, 1, 0))):
        with Locations(Location((57.5, -20, 0), (0, 0, 270))):
            Circle(SQUARE_FLANGE_HOLE_2_SKETCH_R)
    extrude(amount=-SQUARE_FLANGE_HOLE_2_5_DEPTH, mode=Mode.SUBTRACT)

    # Square Flange Hole 3 Sketch → Square Flange Hole 3 _5 (cut)
    with BuildSketch(Plane(origin=(0, 65, 0), x_dir=(1, 0, 0), z_dir=(0, 1, 0))):
        with Locations(Location((97.5, 20, 0), (0, 0, 270))):
            Circle(SQUARE_FLANGE_HOLE_3_SKETCH_R)
    extrude(amount=-SQUARE_FLANGE_HOLE_3_5_DEPTH, mode=Mode.SUBTRACT)

    # Square Flange Hole 4 Sketch → Square Flange Hole 4 _5 (cut)
    with BuildSketch(Plane(origin=(0, 65, 0), x_dir=(1, 0, 0), z_dir=(0, 1, 0))):
        with Locations(Location((97.5, -20, 0), (0, 0, 270))):
            Circle(SQUARE_FLANGE_HOLE_4_SKETCH_R)
    extrude(amount=-SQUARE_FLANGE_HOLE_4_5_DEPTH, mode=Mode.SUBTRACT)

    # Round Flange Hole 1 Sketch → Round Flange Hole 1 _5 (cut)
    with BuildSketch(Plane.ZY):
        with Locations((0, -23.75)):
            Circle(ROUND_FLANGE_HOLE_1_SKETCH_R)
    extrude(amount=-ROUND_FLANGE_HOLE_1_5_DEPTH, mode=Mode.SUBTRACT)

    # Round Flange Hole 2 Sketch → Round Flange Hole 2 _5 (cut)
    with BuildSketch(Plane.ZY):
        with Locations((-23.75, 0)):
            Circle(ROUND_FLANGE_HOLE_2_SKETCH_R)
    extrude(amount=-ROUND_FLANGE_HOLE_2_5_DEPTH, mode=Mode.SUBTRACT)

    # Round Flange Hole 3 Sketch → Round Flange Hole 3 _5 (cut)
    with BuildSketch(Plane.ZY):
        with Locations((0, 23.75)):
            Circle(ROUND_FLANGE_HOLE_3_SKETCH_R)
    extrude(amount=-ROUND_FLANGE_HOLE_3_5_DEPTH, mode=Mode.SUBTRACT)

    # Round Flange Hole 4 Sketch → Round Flange Hole 4 _5 (cut)
    with BuildSketch(Plane.ZY):
        with Locations((23.75, 0)):
            Circle(ROUND_FLANGE_HOLE_4_SKETCH_R)
    extrude(amount=-ROUND_FLANGE_HOLE_4_5_DEPTH, mode=Mode.SUBTRACT)

    # Side Pipe _20: up to this cylinder (the profile starts outside it)
    side_pipe_20_end = Plane(origin=(77.5, 39.375, 0), z_dir=(0, 1, 0)) * Cylinder(SIDE_PIPE_20_END_RADIUS, 347.118, mode=Mode.PRIVATE)
    # Side Pipe Sketch → Side Pipe _20 (add, up to the surface)
    with BuildSketch(Plane(origin=(140, 39.375, 0), x_dir=(0, 0, -1), z_dir=(1, 0, 0)), mode=Mode.PRIVATE) as side_pipe_20_sk1:
        Circle(SIDE_PIPE_SKETCH_R)
    side_pipe_20_tool1 = extrude(side_pipe_20_sk1.sketch, amount=-SIDE_PIPE_20_REACH, mode=Mode.PRIVATE) - side_pipe_20_end
    add(side_pipe_20_tool1.solids().sort_by_distance((140, 39.375, 0))[0])

    # Side Pipe Bore Sketch → Side Pipe Bore _15 (cut)
    with BuildSketch(Plane(origin=(140, 0, 0), x_dir=(0, 0, -1), z_dir=(1, 0, 0))):
        with Locations((0, 39.375)):
            Circle(SIDE_PIPE_BORE_SKETCH_R)
    extrude(amount=-SIDE_PIPE_BORE_15_DEPTH, mode=Mode.SUBTRACT)


solid = part_3.part
